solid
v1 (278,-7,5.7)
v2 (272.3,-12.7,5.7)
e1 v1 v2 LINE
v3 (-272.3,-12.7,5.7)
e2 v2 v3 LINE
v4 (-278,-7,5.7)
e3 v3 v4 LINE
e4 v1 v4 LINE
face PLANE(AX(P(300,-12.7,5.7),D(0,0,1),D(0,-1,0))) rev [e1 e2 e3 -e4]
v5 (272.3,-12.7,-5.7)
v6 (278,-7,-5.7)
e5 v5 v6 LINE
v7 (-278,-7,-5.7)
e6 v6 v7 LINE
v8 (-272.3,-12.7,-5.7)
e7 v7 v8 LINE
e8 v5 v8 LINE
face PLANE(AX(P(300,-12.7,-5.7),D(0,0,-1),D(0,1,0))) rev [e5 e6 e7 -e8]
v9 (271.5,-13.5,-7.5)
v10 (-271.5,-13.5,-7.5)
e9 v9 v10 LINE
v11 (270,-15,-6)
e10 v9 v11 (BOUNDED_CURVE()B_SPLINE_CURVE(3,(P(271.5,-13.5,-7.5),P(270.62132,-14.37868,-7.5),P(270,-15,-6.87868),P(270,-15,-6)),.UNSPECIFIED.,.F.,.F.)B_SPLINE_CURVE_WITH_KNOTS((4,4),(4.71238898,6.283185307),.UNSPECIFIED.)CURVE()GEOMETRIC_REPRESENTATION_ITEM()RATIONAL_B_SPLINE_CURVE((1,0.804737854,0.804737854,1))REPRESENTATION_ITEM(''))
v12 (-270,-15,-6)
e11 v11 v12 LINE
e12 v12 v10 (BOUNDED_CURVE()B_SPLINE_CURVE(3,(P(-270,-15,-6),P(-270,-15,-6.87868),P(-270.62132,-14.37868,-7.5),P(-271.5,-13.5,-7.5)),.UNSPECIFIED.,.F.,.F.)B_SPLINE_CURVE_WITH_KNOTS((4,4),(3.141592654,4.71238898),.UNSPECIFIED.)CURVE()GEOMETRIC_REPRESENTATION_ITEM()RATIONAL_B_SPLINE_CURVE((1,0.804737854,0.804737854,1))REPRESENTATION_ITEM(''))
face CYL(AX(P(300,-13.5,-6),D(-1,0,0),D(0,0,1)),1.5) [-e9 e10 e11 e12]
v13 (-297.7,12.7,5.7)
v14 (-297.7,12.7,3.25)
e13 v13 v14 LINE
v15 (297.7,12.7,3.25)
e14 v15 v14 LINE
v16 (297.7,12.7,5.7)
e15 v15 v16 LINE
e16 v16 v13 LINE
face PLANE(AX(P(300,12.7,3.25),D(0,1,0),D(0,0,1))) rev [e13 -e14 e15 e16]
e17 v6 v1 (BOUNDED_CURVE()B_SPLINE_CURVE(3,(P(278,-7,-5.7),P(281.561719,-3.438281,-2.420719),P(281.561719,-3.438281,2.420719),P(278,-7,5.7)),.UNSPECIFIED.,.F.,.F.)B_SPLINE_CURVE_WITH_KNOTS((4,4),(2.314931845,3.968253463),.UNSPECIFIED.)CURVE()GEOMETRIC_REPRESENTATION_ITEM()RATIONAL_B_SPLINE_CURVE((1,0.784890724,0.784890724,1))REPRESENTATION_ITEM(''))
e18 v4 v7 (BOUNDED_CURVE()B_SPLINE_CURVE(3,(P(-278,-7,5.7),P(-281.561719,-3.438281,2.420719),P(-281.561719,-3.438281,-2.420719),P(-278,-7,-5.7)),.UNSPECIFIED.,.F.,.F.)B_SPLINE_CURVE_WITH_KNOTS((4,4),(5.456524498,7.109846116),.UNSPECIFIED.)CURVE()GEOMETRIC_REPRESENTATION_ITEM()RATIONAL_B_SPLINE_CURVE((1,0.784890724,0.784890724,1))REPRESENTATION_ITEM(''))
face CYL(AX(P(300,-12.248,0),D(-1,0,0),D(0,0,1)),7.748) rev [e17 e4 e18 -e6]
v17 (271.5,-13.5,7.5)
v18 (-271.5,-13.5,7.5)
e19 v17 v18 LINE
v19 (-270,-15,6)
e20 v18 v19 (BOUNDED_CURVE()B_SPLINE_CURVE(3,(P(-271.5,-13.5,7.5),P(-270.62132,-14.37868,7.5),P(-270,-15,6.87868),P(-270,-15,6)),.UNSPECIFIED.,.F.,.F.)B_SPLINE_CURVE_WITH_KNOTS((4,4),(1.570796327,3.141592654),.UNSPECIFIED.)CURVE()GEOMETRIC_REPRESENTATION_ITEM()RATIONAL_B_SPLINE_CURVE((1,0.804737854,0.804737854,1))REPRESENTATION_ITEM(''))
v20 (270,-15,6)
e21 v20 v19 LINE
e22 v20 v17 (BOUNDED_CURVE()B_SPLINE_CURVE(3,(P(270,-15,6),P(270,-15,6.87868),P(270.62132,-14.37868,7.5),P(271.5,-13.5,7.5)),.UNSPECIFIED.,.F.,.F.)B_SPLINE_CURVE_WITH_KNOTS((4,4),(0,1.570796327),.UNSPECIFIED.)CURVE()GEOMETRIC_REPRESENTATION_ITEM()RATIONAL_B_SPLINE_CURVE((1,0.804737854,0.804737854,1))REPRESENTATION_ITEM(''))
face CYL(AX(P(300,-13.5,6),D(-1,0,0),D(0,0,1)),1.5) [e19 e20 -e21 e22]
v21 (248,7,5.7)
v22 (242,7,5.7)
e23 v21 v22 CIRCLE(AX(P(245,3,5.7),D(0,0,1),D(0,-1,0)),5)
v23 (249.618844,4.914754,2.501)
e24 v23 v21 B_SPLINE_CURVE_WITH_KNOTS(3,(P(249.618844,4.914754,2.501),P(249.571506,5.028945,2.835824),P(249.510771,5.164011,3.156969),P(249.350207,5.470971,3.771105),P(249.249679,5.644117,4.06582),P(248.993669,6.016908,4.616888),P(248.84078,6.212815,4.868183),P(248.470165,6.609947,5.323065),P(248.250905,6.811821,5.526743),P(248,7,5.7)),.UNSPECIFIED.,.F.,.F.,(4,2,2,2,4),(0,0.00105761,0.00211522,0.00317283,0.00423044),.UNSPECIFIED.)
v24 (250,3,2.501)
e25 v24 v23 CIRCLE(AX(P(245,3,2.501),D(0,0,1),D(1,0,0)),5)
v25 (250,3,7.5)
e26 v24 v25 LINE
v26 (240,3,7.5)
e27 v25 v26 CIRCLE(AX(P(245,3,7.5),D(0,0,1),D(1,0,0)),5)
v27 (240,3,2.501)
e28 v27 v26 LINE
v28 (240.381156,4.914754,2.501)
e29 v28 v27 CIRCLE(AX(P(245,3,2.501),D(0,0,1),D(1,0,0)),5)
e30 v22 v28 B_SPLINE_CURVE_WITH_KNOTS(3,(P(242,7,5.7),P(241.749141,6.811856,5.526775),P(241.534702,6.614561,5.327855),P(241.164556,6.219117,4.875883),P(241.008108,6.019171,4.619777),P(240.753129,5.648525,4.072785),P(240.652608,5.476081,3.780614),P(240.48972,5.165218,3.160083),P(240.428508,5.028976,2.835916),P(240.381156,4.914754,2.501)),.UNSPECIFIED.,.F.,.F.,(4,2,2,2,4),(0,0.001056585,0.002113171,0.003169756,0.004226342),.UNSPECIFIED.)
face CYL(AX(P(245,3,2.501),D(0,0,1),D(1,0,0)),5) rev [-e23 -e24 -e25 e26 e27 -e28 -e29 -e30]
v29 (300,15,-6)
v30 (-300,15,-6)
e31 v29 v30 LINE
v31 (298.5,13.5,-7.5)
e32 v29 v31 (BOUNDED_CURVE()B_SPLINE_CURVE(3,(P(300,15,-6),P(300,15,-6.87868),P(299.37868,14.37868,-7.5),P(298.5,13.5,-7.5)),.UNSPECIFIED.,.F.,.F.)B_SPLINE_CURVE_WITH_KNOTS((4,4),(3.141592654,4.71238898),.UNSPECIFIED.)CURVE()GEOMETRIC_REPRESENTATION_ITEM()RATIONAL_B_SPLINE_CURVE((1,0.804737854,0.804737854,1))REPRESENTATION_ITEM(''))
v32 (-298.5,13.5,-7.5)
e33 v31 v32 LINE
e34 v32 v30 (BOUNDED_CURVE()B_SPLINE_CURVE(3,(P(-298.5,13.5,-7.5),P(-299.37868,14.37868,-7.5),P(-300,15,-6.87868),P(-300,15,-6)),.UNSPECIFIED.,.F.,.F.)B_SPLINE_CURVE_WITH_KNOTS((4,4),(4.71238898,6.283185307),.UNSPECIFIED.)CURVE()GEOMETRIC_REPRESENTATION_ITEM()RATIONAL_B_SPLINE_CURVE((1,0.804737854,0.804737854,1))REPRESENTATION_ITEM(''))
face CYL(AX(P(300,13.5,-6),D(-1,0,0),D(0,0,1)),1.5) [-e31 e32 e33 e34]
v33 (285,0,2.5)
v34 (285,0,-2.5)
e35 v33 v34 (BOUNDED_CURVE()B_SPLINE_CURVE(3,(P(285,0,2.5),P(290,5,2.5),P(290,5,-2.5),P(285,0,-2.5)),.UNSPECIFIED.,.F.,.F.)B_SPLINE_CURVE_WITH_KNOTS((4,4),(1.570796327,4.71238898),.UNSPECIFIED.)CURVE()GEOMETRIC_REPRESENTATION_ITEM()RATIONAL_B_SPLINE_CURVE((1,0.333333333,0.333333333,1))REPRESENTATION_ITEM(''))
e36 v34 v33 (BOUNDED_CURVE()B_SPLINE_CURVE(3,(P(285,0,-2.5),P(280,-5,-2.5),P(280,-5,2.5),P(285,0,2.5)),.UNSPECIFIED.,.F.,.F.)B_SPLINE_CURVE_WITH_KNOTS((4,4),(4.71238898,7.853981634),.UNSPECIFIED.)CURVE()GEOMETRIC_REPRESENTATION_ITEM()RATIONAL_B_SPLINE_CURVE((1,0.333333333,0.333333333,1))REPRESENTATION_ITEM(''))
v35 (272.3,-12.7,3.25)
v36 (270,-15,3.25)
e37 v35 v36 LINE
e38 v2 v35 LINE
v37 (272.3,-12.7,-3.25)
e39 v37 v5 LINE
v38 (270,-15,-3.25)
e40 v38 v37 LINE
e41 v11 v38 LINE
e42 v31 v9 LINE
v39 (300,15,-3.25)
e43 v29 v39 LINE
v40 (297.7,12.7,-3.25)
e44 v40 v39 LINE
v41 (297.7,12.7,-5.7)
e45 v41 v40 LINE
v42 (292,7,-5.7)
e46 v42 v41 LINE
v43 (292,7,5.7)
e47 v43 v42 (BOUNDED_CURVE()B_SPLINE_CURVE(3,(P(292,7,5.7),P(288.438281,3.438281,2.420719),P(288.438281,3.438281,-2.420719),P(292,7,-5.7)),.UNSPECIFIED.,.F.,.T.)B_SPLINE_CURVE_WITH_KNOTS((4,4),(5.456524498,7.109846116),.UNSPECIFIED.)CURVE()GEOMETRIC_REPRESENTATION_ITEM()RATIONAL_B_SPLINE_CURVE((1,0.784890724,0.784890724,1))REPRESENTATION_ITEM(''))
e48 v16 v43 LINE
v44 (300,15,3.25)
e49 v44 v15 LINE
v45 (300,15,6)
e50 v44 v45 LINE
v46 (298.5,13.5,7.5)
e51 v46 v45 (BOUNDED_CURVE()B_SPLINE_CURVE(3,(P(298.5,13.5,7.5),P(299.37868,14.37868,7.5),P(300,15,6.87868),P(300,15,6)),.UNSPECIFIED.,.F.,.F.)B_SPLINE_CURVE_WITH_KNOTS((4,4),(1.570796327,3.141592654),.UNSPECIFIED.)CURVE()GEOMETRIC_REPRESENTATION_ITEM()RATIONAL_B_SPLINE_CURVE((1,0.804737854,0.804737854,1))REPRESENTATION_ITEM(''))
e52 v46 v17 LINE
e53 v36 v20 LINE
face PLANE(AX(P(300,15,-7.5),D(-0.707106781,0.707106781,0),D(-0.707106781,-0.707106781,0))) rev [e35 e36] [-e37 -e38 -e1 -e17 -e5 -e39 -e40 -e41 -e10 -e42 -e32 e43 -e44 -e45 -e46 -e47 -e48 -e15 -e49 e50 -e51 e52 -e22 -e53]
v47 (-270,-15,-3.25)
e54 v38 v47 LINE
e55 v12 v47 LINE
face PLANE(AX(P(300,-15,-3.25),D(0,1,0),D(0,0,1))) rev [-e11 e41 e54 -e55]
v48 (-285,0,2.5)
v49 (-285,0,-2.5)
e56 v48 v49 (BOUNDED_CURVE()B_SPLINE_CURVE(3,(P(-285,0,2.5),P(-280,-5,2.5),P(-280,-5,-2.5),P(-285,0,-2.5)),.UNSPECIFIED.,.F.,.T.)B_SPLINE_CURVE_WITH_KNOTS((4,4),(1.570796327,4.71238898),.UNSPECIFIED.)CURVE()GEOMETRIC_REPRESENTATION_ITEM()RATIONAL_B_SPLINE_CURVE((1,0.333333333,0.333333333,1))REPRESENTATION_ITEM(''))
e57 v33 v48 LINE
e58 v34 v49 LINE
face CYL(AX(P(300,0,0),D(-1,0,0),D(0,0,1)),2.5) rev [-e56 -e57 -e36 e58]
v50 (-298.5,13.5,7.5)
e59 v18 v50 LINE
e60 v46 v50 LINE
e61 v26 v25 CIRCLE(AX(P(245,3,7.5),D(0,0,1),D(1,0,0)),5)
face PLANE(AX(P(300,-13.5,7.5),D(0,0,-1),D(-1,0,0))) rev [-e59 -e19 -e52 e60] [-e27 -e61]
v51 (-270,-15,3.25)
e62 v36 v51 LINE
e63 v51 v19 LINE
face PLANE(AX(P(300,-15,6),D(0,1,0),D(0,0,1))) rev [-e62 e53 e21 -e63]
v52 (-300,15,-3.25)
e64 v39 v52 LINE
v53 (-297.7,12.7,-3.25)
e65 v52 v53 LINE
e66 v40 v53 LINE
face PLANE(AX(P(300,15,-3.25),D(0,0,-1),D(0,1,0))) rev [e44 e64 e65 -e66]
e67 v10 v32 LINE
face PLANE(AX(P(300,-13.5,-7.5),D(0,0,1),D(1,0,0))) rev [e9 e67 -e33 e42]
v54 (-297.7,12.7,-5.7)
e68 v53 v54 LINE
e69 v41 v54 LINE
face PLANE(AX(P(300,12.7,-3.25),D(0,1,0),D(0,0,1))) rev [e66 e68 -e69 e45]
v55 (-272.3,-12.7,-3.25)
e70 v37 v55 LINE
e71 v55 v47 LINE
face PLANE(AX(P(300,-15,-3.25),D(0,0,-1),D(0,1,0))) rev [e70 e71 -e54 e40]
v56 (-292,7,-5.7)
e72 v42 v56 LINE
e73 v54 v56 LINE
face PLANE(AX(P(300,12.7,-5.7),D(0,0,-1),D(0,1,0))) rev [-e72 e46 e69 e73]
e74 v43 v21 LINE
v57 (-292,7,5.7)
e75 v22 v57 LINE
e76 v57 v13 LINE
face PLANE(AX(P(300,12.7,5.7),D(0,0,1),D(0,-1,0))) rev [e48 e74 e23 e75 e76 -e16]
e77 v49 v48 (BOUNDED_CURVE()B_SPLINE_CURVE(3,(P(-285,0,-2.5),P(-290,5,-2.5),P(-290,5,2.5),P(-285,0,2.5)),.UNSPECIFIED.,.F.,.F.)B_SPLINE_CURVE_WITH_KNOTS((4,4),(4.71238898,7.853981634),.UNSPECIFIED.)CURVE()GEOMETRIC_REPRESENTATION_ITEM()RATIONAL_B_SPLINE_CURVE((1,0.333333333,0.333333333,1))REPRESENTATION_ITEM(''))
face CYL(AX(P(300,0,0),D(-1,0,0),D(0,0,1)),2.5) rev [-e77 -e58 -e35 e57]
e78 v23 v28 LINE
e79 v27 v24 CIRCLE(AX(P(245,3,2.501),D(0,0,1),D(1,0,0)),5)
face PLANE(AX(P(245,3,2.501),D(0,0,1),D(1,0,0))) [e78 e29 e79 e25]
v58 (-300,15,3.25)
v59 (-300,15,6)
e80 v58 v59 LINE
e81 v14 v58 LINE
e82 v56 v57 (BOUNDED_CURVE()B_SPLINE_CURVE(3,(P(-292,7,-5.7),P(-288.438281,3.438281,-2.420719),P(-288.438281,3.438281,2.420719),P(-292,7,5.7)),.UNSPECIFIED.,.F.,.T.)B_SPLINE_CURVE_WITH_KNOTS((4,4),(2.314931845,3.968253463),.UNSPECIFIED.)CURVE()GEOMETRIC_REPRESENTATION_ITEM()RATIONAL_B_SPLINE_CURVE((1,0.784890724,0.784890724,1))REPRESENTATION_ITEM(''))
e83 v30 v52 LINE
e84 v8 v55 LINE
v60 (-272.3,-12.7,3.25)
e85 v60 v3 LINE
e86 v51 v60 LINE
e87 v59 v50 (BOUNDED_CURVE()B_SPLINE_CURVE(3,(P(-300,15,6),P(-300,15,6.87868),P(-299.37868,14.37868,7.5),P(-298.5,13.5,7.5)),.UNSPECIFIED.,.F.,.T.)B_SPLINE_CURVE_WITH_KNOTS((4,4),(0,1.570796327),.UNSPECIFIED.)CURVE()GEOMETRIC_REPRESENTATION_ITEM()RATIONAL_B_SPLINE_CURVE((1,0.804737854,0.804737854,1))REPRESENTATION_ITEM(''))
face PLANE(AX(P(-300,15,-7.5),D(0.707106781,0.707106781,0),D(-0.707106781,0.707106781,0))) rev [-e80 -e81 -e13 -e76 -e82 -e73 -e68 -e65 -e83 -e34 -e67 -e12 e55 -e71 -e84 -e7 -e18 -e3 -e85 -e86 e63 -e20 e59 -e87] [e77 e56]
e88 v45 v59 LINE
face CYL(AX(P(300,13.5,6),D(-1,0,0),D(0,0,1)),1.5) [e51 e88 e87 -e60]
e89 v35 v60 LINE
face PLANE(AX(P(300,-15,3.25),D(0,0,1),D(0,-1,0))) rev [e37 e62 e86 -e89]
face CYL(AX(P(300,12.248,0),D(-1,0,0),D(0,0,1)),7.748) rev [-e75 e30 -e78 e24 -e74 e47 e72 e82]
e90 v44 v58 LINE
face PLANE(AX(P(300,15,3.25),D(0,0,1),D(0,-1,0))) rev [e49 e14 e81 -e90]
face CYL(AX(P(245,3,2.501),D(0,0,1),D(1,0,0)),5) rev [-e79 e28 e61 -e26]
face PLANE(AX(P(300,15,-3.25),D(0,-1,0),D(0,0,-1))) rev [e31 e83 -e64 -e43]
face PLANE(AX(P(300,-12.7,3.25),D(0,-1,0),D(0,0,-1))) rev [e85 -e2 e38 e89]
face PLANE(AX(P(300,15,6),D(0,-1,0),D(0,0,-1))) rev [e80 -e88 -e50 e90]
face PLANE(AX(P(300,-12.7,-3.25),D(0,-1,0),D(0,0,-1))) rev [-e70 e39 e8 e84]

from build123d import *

# Parameters (mm, degrees)
SKETCH12_R          = 2.5
MEMBER_1_DEPTH      = 600
CUT_EXTRUDE_1_DEPTH = 301.749064836
SKETCH_7_R          = 5
CUT_EXTRUDE_2_DEPTH = 4.999


with BuildPart() as part:
    # Sketch12 → Member 1 (new body)
    with BuildSketch(Plane(origin=(-300, 0, 0), x_dir=(0, 0, -1), z_dir=(1, 0, 0))):
        with BuildLine():
            Line((-6, -15), (-3.25, -15))
            Line((-3.25, -15), (-3.25, -12.7))
            Line((-3.25, -12.7), (-5.7, -12.7))
            Line((-5.7, -12.7), (-5.7, -7))
            ThreePointArc((-5.7, -7), (0, -4.5), (5.7, -7))
            Line((5.7, -7), (5.7, -12.7))
            Line((5.7, -12.7), (3.25, -12.7))
            Line((3.25, -12.7), (3.25, -15))
            Line((3.25, -15), (6, -15))
            ThreePointArc((6, -15), (7.060660172, -14.560660172), (7.5, -13.5))
            Line((7.5, -13.5), (7.5, 13.5))
            ThreePointArc((7.5, 13.5), (7.060660172, 14.560660172), (6, 15))
            Line((6, 15), (3.25, 15))
            Line((3.25, 15), (3.25, 12.7))
            Line((3.25, 12.7), (5.7, 12.7))
            Line((5.7, 12.7), (5.7, 7))
            ThreePointArc((5.7, 7), (0, 4.5), (-5.7, 7))
            Line((-5.7, 7), (-5.7, 12.7))
            Line((-5.7, 12.7), (-3.25, 12.7))
            Line((-3.25, 12.7), (-3.25, 15))
            Line((-3.25, 15), (-6, 15))
            ThreePointArc((-6, 15), (-7.060660172, 14.560660172), (-7.5, 13.5))
            Line((-7.5, 13.5), (-7.5, -13.5))
            ThreePointArc((-7.5, -13.5), (-7.060660172, -14.560660172), (-6, -15))
        make_face()
        Circle(SKETCH12_R, mode=Mode.SUBTRACT)
    extrude(amount=MEMBER_1_DEPTH)

    # 草图4 → 切除-拉伸1 (cut, through all)
    with BuildSketch(Plane.XY.offset(7.5)):
        Polygon((-300, 15), (-270, -15), (-300, -15), align=None)
        Polygon((300, -15), (300, 15), (270, -15), align=None)
    extrude(amount=-CUT_EXTRUDE_1_DEPTH, mode=Mode.SUBTRACT)

    # 草图7 → 切除-拉伸2 (cut)
    with BuildSketch(Plane.XY.offset(7.5)):
        with Locations((245, 3)):
            Circle(SKETCH_7_R)
    extrude(amount=-CUT_EXTRUDE_2_DEPTH, mode=Mode.SUBTRACT)


solid = part.part
